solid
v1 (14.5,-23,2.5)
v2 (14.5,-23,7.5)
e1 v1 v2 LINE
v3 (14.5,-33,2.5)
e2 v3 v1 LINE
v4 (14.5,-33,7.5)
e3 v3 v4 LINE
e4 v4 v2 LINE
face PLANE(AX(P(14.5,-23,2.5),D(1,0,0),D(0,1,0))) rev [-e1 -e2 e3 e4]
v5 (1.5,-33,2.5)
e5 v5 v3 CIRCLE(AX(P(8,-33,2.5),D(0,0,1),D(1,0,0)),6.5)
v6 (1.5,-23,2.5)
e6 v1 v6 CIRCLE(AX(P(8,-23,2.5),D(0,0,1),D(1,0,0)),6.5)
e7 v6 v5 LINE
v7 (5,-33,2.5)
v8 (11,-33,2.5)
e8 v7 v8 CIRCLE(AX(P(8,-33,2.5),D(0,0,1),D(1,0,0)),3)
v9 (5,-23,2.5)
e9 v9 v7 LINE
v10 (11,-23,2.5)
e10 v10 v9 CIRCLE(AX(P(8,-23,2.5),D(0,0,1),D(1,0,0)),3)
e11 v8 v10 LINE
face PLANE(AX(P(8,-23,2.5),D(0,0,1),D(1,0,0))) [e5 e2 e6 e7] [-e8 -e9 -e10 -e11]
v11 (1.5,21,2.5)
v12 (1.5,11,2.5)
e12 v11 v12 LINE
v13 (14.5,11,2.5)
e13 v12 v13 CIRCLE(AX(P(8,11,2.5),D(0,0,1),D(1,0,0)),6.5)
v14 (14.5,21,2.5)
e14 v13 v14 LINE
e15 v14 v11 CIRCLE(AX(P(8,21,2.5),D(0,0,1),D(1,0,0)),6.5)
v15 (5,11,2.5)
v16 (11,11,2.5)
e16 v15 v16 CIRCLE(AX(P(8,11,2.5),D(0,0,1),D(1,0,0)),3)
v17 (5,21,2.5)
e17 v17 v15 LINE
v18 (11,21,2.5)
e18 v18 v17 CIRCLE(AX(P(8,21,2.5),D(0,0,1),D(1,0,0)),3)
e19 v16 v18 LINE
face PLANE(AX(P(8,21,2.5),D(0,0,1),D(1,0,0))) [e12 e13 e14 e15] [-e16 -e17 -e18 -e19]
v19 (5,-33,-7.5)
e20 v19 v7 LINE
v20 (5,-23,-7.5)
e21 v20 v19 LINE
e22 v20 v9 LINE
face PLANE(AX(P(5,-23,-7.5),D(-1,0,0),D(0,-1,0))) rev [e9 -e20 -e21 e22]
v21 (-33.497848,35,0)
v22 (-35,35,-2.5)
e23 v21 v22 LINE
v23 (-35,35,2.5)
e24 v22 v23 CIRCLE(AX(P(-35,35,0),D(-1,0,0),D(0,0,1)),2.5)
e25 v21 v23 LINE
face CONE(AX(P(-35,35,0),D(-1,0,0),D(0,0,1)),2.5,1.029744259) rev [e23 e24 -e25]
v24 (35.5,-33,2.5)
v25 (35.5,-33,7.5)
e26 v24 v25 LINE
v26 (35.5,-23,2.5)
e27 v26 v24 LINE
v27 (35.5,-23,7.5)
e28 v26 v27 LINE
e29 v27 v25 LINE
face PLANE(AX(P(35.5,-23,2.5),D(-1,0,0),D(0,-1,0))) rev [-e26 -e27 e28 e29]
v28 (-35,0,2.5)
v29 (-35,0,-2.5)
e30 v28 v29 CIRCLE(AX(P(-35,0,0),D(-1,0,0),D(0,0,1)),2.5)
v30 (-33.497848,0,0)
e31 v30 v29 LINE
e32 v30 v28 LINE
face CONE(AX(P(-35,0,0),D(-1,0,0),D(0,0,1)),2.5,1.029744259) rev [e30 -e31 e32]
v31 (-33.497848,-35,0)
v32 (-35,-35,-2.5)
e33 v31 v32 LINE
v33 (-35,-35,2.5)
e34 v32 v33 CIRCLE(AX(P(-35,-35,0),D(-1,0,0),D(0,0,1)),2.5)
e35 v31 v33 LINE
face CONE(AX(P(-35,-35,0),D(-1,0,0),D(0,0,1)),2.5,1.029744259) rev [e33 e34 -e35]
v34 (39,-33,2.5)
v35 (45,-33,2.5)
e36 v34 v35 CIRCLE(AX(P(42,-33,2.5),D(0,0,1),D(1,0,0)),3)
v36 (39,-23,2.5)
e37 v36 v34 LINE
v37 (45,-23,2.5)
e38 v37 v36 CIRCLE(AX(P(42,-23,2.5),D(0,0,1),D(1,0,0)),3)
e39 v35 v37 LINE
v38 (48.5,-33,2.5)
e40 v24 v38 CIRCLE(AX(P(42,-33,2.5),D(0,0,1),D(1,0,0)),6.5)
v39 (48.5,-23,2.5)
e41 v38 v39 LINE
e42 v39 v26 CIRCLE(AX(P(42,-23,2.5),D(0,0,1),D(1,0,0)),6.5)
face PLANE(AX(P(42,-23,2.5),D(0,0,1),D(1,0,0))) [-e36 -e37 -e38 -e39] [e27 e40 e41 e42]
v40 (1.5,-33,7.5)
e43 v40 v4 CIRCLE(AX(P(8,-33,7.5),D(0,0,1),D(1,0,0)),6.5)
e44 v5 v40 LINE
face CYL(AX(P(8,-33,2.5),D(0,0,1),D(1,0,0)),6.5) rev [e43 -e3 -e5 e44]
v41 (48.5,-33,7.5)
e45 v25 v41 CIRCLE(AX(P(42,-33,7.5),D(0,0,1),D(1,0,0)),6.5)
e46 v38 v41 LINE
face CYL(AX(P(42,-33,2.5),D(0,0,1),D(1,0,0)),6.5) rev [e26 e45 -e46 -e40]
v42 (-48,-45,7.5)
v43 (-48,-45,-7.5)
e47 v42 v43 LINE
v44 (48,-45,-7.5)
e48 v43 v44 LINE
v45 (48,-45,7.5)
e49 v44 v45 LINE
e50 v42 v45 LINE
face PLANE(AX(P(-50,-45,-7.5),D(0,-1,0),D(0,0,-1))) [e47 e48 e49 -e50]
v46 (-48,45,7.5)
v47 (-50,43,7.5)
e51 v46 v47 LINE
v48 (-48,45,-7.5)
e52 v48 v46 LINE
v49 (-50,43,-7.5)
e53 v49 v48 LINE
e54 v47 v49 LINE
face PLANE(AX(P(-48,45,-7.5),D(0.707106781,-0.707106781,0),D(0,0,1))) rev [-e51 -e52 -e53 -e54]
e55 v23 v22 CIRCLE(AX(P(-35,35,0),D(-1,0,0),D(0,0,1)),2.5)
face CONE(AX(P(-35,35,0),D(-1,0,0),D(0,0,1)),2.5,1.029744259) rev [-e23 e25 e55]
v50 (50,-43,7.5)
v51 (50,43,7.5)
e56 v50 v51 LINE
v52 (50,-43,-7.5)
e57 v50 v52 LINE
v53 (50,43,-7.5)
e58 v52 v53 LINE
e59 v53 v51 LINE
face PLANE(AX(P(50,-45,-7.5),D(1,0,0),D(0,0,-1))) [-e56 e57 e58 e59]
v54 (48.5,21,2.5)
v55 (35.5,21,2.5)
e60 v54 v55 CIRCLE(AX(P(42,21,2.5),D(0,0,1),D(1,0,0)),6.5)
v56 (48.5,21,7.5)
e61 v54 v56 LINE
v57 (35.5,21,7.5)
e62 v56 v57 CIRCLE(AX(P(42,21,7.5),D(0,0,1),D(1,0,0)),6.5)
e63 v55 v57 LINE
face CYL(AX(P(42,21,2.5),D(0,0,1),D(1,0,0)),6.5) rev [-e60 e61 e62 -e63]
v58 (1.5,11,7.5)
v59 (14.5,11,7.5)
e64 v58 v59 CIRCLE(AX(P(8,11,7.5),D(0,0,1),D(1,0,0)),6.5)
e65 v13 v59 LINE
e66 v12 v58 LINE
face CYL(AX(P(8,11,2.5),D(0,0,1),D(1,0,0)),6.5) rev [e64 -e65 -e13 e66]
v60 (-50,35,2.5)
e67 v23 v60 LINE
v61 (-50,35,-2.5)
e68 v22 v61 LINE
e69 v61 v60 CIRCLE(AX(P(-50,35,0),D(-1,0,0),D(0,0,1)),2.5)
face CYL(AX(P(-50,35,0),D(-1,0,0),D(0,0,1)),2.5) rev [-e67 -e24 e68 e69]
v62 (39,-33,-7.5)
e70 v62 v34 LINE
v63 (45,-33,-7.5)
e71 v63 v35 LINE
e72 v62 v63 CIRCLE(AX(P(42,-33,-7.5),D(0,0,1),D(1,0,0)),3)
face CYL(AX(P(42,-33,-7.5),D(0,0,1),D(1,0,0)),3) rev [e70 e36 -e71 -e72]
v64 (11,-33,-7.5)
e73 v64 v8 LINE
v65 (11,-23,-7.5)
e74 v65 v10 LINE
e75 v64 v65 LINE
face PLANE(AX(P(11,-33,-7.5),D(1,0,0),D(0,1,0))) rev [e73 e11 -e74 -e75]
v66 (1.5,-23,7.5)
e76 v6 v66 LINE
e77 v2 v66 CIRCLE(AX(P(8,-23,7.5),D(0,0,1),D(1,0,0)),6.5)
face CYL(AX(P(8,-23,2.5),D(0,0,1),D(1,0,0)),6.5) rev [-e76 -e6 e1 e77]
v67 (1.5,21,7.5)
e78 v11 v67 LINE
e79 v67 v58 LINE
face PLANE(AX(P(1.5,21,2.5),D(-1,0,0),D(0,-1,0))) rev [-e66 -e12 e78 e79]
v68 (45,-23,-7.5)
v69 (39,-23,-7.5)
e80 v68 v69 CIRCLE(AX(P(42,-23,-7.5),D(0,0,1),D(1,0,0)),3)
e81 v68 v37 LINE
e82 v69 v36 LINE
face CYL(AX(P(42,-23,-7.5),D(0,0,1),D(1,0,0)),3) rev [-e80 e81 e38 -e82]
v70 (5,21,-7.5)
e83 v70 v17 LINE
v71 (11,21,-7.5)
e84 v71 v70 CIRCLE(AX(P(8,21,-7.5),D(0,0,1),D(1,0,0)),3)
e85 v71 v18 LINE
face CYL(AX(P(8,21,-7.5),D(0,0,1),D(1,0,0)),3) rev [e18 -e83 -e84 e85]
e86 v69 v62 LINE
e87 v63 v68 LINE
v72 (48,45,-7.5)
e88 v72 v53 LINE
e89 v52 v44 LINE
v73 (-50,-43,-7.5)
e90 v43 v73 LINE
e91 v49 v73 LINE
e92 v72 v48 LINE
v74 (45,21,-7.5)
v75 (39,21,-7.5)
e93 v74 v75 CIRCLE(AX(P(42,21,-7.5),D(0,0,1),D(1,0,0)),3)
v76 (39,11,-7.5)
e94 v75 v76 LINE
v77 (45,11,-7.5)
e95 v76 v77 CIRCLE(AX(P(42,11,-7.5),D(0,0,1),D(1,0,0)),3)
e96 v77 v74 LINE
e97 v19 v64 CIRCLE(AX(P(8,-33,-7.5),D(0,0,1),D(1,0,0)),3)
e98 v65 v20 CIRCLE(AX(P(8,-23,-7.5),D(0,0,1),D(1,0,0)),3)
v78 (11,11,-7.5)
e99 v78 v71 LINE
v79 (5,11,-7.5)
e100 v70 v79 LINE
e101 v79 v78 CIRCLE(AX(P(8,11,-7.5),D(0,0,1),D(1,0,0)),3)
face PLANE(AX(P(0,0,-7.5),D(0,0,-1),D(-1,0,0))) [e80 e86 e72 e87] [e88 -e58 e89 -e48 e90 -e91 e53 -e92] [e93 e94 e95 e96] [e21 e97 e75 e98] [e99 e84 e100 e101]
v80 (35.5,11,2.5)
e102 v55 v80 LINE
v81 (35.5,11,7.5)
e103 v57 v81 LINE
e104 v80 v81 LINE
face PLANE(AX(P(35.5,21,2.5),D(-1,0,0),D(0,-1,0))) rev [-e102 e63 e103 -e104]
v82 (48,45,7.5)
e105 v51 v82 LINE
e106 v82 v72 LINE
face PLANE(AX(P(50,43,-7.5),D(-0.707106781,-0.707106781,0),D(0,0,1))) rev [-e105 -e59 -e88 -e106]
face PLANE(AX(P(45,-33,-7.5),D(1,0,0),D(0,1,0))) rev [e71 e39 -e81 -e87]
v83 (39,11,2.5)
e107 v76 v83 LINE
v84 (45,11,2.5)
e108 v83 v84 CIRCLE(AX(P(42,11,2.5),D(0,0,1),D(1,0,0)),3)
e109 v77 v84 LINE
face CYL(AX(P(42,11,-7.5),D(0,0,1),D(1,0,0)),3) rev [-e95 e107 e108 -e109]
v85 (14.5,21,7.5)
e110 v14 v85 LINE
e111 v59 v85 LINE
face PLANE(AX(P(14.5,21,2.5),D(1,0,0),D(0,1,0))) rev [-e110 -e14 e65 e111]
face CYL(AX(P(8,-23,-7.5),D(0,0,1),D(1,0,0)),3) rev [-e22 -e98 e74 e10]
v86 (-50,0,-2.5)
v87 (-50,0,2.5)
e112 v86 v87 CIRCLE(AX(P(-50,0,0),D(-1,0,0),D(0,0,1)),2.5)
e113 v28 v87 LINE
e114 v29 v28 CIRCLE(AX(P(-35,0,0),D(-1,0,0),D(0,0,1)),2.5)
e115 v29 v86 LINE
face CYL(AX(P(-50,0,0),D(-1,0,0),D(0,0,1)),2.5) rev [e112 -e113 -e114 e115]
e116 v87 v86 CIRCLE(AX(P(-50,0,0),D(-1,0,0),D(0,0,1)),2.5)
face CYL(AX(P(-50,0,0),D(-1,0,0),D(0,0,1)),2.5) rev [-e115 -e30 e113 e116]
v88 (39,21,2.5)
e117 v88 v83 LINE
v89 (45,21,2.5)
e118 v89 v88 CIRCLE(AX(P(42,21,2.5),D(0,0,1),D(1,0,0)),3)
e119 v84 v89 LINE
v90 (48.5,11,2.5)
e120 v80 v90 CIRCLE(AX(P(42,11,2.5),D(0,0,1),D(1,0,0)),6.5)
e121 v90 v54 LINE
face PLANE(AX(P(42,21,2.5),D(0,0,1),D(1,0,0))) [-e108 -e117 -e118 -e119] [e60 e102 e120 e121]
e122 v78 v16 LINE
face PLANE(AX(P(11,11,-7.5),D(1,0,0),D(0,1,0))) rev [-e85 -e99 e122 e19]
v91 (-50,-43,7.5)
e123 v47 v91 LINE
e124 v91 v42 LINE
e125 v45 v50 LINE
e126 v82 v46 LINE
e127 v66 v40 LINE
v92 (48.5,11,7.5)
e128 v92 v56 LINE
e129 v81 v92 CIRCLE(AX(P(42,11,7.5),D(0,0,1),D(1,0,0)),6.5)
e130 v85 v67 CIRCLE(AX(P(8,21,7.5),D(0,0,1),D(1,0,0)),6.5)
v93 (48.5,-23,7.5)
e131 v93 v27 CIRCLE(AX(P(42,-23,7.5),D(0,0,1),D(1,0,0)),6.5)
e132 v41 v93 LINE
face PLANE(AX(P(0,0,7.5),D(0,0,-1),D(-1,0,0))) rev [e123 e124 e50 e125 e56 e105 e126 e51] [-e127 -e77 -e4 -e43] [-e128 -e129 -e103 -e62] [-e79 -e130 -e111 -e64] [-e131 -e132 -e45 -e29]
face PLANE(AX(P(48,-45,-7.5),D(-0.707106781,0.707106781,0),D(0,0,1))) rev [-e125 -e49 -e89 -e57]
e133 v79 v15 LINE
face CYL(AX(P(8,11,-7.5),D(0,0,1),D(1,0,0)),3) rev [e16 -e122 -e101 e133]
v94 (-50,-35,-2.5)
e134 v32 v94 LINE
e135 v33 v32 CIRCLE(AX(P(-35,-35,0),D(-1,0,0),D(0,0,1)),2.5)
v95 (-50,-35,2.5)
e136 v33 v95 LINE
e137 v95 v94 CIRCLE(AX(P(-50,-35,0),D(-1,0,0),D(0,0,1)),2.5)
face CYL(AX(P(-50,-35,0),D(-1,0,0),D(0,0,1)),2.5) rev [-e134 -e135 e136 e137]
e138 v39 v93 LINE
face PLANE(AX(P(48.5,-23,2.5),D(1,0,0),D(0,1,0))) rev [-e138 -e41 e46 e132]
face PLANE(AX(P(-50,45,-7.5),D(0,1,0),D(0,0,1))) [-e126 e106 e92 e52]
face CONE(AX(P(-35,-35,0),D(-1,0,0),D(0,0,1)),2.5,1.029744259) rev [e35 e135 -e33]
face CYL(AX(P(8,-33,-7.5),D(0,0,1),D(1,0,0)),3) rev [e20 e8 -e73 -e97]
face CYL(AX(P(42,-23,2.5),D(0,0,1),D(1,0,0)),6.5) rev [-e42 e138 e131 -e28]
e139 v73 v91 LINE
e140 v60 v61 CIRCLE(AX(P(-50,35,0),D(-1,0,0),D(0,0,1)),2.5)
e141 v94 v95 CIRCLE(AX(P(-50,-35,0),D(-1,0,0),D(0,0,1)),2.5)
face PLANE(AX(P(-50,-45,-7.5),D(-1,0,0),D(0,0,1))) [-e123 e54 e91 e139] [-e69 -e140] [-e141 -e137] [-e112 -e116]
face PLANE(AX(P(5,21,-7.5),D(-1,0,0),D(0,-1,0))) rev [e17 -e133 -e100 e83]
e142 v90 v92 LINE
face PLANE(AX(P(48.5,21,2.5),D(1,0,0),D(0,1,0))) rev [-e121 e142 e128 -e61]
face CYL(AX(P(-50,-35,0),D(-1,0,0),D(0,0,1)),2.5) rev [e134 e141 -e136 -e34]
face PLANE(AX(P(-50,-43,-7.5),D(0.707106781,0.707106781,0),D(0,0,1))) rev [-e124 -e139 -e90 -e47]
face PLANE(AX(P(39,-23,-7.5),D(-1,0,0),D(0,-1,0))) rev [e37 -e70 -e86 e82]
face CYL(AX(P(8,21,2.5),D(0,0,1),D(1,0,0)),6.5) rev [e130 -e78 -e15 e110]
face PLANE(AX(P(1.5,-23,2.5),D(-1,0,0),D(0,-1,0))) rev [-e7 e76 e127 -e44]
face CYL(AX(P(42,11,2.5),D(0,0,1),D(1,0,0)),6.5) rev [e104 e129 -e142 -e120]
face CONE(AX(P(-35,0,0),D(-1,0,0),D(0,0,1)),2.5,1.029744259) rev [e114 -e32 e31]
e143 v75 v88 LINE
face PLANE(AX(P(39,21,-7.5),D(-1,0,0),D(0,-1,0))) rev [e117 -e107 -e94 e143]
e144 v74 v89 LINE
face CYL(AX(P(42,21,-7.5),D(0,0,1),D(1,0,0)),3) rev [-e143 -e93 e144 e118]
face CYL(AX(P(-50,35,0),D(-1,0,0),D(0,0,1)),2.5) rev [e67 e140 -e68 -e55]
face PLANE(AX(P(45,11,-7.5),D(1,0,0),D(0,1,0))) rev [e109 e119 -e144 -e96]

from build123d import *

# Parameters (mm, degrees)
SKETCH_1_W                  = 100
SKETCH_1_H                  = 90
EXTRUDE_1_DEPTH             = 7.5
HOLE_WIZARD_M6_1_D          = 5
HOLE_WIZARD_M6_1_DEPTH      = 15
HOLE_WIZARD_M6_1_TIP        = 1.502151548
CUT_EXTRUDE_1_DEPTH         = 5
CUT_EXTRUDE_2_DEPTH         = 69.007352544
PATTERN_LINEAR_1_COUNT      = 2
PATTERN_LINEAR_1_PITCH      = 34
PATTERN_LINEAR_1_COUNT_DIR2 = 2
PATTERN_LINEAR_1_PITCH_DIR2 = 44
CHAMFER_1_SIZE              = 2


with BuildPart() as part:
    # 草图1 → 凸台-拉伸1 (new, symmetric)
    with BuildSketch(Plane.XY):
        Rectangle(SKETCH_1_W, SKETCH_1_H)
    extrude(amount=EXTRUDE_1_DEPTH, both=True)

    # M6 螺纹孔1
    with Locations(Plane.ZY.offset(50)):
        with Locations((0, 35), (0, 0), (0, -35)):
            Hole(HOLE_WIZARD_M6_1_D / 2, depth=HOLE_WIZARD_M6_1_DEPTH)
            with Locations((0, 0, -(HOLE_WIZARD_M6_1_DEPTH + HOLE_WIZARD_M6_1_TIP / 2))):  # 118° drill point
                Cone(0, HOLE_WIZARD_M6_1_D / 2, HOLE_WIZARD_M6_1_TIP, mode=Mode.SUBTRACT)

    # 草图4 → 切除-拉伸1 (cut)
    with BuildSketch(Plane.XY.offset(7.5)):
        with BuildLine():
            Line((14.5, -23), (14.5, -33))
            ThreePointArc((14.5, -33), (8, -39.5), (1.5, -33))
            Line((1.5, -33), (1.5, -23))
            ThreePointArc((1.5, -23), (8, -16.5), (14.5, -23))
        make_face()
    cut_extrude_1 = extrude(amount=-CUT_EXTRUDE_1_DEPTH, mode=Mode.SUBTRACT)

    # 草图5 → 切除-拉伸2 (cut, through all)
    with BuildSketch(Plane.XY.offset(2.5)):
        with BuildLine():
            Line((5, -23), (5, -33))
            ThreePointArc((5, -33), (8, -36), (11, -33))
            Line((11, -33), (11, -23))
            ThreePointArc((11, -23), (8, -20), (5, -23))
        make_face()
    cut_extrude_2 = extrude(amount=-CUT_EXTRUDE_2_DEPTH, mode=Mode.SUBTRACT)

    # 阵列(线性)1: 切除-拉伸1, Cut-Extrude 2 2 × 2
    with Locations(*[(i * PATTERN_LINEAR_1_PITCH, j * PATTERN_LINEAR_1_PITCH_DIR2, 0) for i in range(PATTERN_LINEAR_1_COUNT) for j in range(PATTERN_LINEAR_1_COUNT_DIR2) if (i, j) != (0, 0)]):
        add(cut_extrude_1, mode=Mode.SUBTRACT)
        add(cut_extrude_2, mode=Mode.SUBTRACT)

    # 倒角1
    chamfer_1_edges = [part.edges().sort_by_distance(p)[0] for p in [
        (50, -45, 0),
        (-50, -45, 0),
        (-50, 45, 0),
        (50, 45, 0),
    ]]
    chamfer(chamfer_1_edges, length=CHAMFER_1_SIZE)


solid = part.part
